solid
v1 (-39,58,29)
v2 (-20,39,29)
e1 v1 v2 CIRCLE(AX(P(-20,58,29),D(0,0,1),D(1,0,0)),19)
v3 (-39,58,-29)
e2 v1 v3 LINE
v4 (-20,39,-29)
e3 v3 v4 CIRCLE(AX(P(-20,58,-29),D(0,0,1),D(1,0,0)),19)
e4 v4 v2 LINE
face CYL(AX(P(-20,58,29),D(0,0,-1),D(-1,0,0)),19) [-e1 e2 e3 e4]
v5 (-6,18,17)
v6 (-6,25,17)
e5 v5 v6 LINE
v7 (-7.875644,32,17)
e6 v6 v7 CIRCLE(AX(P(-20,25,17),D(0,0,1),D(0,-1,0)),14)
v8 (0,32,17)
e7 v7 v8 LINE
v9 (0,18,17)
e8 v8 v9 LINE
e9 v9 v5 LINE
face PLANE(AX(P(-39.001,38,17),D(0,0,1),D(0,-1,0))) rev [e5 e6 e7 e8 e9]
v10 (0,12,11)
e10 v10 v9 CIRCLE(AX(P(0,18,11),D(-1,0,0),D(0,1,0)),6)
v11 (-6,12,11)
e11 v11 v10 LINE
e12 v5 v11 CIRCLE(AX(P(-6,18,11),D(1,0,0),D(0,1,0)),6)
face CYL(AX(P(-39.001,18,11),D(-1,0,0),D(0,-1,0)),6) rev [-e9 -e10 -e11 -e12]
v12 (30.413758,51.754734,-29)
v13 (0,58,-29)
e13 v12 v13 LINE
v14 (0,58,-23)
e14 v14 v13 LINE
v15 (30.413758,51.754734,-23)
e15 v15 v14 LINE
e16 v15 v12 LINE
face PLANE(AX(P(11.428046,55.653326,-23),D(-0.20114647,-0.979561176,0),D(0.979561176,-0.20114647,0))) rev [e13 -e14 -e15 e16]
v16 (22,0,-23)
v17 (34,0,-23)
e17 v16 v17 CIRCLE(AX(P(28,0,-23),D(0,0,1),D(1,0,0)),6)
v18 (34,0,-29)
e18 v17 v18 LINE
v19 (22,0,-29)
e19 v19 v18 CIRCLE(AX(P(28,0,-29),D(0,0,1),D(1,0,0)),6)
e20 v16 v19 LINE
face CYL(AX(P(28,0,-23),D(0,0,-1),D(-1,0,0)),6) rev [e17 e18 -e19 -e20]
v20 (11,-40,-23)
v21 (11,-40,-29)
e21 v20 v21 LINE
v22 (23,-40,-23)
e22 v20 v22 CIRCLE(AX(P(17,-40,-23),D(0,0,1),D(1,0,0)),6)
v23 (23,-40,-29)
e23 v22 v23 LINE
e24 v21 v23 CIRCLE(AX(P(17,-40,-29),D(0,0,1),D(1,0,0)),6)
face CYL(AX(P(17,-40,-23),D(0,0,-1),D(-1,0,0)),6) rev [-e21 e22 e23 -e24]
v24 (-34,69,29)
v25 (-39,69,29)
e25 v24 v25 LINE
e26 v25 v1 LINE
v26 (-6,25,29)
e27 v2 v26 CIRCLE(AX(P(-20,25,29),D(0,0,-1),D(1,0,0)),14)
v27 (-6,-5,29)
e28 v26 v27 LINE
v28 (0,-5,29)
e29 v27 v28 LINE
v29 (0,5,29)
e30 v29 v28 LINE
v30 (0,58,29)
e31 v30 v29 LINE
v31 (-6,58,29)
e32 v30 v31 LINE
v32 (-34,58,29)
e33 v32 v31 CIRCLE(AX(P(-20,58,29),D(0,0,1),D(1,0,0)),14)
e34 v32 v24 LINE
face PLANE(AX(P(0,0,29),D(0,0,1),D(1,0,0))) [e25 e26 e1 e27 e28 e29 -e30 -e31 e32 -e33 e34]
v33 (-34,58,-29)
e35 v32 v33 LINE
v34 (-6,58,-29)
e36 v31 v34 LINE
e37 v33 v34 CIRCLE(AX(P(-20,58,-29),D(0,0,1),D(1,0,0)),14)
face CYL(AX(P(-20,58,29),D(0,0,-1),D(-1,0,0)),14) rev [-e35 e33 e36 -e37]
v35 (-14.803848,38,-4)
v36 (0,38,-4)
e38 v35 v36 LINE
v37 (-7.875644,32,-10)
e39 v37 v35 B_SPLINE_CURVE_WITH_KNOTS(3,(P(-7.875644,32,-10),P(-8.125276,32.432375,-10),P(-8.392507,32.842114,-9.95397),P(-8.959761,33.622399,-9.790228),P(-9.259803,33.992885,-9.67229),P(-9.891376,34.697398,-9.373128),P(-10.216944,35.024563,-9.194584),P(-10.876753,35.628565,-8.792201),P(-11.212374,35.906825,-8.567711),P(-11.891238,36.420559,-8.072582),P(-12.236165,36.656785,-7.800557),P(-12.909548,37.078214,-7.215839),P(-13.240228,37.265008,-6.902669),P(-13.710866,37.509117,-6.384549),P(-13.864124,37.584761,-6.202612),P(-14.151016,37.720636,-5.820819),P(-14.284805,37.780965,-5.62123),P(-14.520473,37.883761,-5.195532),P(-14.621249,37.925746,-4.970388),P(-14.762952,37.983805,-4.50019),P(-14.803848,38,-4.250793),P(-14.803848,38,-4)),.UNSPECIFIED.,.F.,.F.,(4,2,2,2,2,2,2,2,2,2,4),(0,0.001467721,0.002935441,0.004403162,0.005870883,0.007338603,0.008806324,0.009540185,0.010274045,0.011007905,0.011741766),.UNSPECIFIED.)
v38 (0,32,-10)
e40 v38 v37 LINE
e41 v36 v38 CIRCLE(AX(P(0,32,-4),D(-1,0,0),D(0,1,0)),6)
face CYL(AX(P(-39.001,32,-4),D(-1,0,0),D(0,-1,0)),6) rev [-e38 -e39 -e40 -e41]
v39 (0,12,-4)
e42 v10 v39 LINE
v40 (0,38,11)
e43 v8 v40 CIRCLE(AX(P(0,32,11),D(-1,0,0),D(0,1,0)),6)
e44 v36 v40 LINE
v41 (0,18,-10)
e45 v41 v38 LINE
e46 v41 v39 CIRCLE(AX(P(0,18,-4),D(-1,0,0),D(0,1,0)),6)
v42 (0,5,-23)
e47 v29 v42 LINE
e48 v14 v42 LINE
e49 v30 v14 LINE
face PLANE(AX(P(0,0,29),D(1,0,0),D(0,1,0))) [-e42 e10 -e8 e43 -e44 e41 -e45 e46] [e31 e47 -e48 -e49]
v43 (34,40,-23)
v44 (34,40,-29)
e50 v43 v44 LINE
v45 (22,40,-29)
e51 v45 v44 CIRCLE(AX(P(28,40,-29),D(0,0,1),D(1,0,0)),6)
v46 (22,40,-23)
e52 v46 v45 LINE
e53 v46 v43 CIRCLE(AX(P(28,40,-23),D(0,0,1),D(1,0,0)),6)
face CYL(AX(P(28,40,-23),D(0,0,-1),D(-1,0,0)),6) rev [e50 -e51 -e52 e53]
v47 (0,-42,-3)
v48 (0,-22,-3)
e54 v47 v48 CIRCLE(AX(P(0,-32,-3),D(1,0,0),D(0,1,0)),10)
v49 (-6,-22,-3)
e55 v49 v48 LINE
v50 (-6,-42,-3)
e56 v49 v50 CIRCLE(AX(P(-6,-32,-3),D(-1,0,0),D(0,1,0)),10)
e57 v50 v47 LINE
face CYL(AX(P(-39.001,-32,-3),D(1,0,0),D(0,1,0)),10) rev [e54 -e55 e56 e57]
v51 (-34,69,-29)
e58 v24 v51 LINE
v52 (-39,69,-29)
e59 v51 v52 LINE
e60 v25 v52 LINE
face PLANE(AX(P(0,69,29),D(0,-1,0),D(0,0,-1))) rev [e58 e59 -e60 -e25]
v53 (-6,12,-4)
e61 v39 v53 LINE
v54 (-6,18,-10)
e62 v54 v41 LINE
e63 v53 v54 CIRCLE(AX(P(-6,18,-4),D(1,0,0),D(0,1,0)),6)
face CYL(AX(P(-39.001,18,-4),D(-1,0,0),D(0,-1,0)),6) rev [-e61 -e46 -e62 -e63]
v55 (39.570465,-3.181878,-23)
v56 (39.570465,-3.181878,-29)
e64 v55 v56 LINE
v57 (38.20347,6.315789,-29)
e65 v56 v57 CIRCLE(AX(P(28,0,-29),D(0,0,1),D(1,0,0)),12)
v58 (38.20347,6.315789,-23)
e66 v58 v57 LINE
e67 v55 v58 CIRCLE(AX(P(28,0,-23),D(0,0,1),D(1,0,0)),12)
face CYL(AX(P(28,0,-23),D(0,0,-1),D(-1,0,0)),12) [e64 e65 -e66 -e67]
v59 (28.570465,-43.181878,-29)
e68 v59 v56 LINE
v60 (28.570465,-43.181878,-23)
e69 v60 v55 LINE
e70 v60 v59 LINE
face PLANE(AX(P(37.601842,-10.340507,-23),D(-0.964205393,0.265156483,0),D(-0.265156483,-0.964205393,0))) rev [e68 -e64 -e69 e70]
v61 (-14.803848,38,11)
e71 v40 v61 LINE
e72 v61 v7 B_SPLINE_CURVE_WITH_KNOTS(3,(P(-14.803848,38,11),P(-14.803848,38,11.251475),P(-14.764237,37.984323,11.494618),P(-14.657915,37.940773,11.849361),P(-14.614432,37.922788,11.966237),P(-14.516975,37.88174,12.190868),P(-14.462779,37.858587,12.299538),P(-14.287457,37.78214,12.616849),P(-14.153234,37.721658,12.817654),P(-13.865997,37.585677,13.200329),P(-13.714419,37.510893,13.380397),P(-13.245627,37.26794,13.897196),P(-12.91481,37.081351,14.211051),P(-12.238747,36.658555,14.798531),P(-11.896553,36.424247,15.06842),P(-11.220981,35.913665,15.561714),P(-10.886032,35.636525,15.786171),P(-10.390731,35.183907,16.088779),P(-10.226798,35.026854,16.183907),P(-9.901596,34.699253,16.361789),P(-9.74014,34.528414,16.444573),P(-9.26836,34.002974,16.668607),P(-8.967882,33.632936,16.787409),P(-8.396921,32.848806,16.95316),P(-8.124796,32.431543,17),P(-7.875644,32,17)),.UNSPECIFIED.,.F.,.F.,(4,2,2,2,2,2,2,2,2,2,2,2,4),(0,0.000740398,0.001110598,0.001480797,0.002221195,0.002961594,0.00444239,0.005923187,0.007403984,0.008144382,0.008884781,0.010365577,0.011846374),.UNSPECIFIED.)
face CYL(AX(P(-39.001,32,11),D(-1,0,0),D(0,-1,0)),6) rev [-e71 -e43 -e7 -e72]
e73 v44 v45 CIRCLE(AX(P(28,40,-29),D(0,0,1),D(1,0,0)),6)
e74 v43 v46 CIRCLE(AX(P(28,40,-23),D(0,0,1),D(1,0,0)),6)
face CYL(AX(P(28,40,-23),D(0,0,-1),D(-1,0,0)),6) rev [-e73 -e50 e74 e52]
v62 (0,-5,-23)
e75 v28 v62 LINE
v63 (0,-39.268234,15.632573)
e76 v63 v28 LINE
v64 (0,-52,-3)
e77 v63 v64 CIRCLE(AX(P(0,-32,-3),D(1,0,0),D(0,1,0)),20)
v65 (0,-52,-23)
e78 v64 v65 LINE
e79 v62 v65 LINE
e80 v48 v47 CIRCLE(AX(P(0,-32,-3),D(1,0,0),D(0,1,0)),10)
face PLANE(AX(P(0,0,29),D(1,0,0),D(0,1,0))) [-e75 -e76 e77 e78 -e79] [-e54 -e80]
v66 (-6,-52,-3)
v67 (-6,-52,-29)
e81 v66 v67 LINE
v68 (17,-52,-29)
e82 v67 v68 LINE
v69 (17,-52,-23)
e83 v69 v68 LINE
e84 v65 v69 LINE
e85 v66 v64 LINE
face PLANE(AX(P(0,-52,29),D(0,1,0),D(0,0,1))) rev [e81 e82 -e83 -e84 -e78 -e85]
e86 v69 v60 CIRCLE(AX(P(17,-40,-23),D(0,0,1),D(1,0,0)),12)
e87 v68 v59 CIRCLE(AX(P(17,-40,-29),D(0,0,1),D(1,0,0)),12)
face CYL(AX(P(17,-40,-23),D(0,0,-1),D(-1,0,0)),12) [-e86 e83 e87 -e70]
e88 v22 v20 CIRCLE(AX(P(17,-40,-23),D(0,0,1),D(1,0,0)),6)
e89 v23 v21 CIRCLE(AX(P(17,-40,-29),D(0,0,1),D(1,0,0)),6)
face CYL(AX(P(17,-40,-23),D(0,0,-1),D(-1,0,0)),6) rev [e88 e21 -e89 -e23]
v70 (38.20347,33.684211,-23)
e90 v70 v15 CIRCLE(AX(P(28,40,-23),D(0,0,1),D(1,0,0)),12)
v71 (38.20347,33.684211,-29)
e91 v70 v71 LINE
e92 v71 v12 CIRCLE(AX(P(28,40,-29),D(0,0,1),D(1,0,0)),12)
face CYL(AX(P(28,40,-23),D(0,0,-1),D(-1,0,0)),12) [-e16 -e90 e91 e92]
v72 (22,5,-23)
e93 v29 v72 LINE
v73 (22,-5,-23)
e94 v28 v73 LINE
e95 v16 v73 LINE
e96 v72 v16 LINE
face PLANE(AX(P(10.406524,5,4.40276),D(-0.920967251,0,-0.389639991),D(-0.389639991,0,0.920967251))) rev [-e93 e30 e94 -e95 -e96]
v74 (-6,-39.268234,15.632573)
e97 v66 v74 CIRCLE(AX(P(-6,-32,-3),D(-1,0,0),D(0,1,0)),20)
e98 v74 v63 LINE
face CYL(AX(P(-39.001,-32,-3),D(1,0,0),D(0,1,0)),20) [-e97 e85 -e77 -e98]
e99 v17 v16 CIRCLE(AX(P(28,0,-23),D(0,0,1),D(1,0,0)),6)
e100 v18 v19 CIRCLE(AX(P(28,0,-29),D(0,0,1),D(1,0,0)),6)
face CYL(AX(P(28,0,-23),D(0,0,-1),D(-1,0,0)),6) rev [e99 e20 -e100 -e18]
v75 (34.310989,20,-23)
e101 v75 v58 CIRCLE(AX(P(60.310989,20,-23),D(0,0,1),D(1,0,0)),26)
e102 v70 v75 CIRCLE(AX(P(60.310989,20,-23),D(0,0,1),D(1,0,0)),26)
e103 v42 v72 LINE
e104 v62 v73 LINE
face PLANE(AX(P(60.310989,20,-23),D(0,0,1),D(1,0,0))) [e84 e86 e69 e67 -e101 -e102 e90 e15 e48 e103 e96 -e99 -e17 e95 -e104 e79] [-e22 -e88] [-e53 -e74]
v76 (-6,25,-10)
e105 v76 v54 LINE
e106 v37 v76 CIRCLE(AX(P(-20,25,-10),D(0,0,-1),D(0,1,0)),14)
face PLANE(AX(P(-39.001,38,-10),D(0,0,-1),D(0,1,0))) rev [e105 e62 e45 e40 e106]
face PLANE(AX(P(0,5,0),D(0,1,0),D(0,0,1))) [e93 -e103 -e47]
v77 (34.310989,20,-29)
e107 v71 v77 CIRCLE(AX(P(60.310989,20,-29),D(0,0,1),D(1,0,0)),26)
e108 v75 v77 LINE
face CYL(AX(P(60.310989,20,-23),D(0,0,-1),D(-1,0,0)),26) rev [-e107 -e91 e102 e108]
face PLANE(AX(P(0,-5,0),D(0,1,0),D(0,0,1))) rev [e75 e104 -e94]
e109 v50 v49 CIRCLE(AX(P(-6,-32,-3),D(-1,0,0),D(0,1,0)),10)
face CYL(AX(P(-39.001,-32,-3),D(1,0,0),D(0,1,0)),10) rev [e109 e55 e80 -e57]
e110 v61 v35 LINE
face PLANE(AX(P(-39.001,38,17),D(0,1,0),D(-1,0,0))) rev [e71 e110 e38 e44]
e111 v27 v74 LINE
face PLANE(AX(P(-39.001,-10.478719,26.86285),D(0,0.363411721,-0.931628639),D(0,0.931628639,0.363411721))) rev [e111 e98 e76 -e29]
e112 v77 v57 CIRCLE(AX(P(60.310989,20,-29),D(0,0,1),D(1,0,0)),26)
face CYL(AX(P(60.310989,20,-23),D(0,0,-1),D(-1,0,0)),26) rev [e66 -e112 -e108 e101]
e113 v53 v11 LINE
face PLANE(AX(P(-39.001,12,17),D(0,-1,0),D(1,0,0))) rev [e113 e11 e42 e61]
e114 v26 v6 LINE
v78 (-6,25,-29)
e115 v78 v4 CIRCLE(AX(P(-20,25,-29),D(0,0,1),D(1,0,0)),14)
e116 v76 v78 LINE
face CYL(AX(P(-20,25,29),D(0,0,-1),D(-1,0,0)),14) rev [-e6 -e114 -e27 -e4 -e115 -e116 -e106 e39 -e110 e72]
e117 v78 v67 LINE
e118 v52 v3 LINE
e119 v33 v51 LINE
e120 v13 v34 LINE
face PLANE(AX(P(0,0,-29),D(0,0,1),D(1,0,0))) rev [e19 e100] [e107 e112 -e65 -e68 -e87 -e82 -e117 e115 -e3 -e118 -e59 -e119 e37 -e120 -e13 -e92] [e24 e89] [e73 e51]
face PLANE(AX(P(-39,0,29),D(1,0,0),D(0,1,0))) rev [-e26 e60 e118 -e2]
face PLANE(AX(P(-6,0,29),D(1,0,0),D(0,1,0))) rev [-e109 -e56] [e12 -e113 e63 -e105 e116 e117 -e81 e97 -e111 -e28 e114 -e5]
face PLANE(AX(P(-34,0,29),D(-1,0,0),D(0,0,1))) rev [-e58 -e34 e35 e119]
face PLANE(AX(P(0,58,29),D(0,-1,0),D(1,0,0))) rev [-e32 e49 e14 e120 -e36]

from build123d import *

# Parameters (mm, degrees)
BRACKET_PROFILE_SKETCH_W  = 5
BRACKET_PROFILE_SKETCH_H  = 11
BRACKET_BODY_DEPTH        = 29
SADDLE_START              = -29
SKETCH1_4_R               = 6
SADDLE_STRAP_DEPTH        = 6
SQUARE_WINDOW_20X20_REACH = 86.865
SQUARE_WINDOW_SKETCH_R    = 10
CENTRE_GUSSET_DEPTH       = 5
CORNER_FILLET_R14_R       = 14
EDGE_NOTCH_REACH          = 86.865
EDGE_NOTCH_SKETCH_W       = 27
EDGE_NOTCH_SKETCH_H       = 26
NOTCH_FILLET_R6_R         = 6


with BuildPart() as part:
    # Bracket Profile Sketch → Bracket Body (new, symmetric)
    with BuildSketch(Plane.XY):
        with BuildLine():
            Line((0, -52), (0, 58))
            Line((0, 58), (-6, 58))
            ThreePointArc((-6, 58), (-20, 44), (-34, 58))
            Line((-34, 58), (-39, 58))
            ThreePointArc((-39, 58), (-26.892024376, 40.29406879), (-6, 45.154767421))
            Line((-6, 45.154767421), (-6, -52))
            Line((-6, -52), (0, -52))
        make_face()
        with Locations((-36.5, 63.5)):
            Rectangle(BRACKET_PROFILE_SKETCH_W, BRACKET_PROFILE_SKETCH_H)
    extrude(amount=BRACKET_BODY_DEPTH, both=True)

    # Sketch1_4 → Saddle Strap (add)
    with BuildSketch(Plane.XY.offset(SADDLE_START)):
        with BuildLine():
            ThreePointArc((38.203470161, 33.684210526), (34.310988843, 20), (38.203470161, 6.315789474))
            ThreePointArc((38.203470161, 6.315789474), (39.877604172, 1.709537694), (39.570464714, -3.181877796))
            Line((39.570464714, -3.181877796), (28.570464714, -43.181877796))
            ThreePointArc((28.570464714, -43.181877796), (24.27383896, -49.544174494), (17, -52))
            Line((17, -52), (0, -52))
            Line((0, -52), (0, 58))
            Line((0, 58), (30.413757643, 51.754734112))
            ThreePointArc((30.413757643, 51.754734112), (39.019735252, 44.750308934), (38.203470161, 33.684210526))
        make_face()
        with Locations((28, 40)):
            Circle(SKETCH1_4_R, mode=Mode.SUBTRACT)
        with Locations((28, 0)):
            Circle(SKETCH1_4_R, mode=Mode.SUBTRACT)
        with Locations((17, -40)):
            Circle(SKETCH1_4_R, mode=Mode.SUBTRACT)
    extrude(amount=SADDLE_STRAP_DEPTH)

    # Square Window Sketch → Square Window 20x20 (cut, up to next)
    with BuildSketch(Plane(origin=(0, 0, 0), x_dir=(0, 0, -1), z_dir=(1, 0, 0)), mode=Mode.PRIVATE) as square_window_20x20_sk1:
        with BuildLine():
            ThreePointArc((3, -52), (-8.283512569, -48.513096139), (-15.632572784, -39.268234411))
            Line((-15.632572784, -39.268234411), (-29, -5))
            Line((-29, -5), (-29, -52))
            Line((-29, -52), (3, -52))
        make_face()
    square_window_20x20_tool1 = extrude(square_window_20x20_sk1.sketch, amount=-SQUARE_WINDOW_20X20_REACH, mode=Mode.PRIVATE) & part.part
    # Square Window Sketch → Square Window 20x20 (cut, up to next)
    with BuildSketch(Plane(origin=(0, 0, 0), x_dir=(0, 0, -1), z_dir=(1, 0, 0)), mode=Mode.PRIVATE) as square_window_20x20_sk2:
        with Locations(Location((3, -32, 0), (0, 0, 90))):
            Circle(SQUARE_WINDOW_SKETCH_R)
    square_window_20x20_tool2 = extrude(square_window_20x20_sk2.sketch, amount=-SQUARE_WINDOW_20X20_REACH, mode=Mode.PRIVATE) & part.part
    add(square_window_20x20_tool1.solids().sort_by_distance((0, -37.269178, 21.871829))[0], mode=Mode.SUBTRACT)
    add(square_window_20x20_tool2.solids().sort_by_distance((0, -32, -3))[0], mode=Mode.SUBTRACT)

    # Centre Gusset Sketch → Centre Gusset (add, symmetric)
    with BuildSketch(Plane(origin=(0, 0, 0), x_dir=(1, 0, 0), z_dir=(0, 1, 0))):
        Polygon((0, 23), (0, -29), (22, 23), align=None)
    extrude(amount=CENTRE_GUSSET_DEPTH, both=True)

    # Corner Fillet R14
    corner_fillet_r14_edges = [part.edges().sort_by_distance(p)[0] for p in [
        (-6, 45.154767421, 0),
    ]]
    fillet(corner_fillet_r14_edges, radius=CORNER_FILLET_R14_R)

    # Edge Notch Sketch → Edge Notch (cut, up to next)
    with BuildSketch(Plane(origin=(0, 0, 0), x_dir=(0, 0, -1), z_dir=(1, 0, 0)), mode=Mode.PRIVATE) as edge_notch_sk1:
        with Locations((-3.5, 25)):
            Rectangle(EDGE_NOTCH_SKETCH_W, EDGE_NOTCH_SKETCH_H)
    edge_notch_tool1 = extrude(edge_notch_sk1.sketch, amount=-EDGE_NOTCH_REACH, mode=Mode.PRIVATE) & part.part
    add(edge_notch_tool1.solids().sort_by_distance((0, 25, 3.5))[0], mode=Mode.SUBTRACT)

    # Notch Fillet R6
    notch_fillet_r6_edges = [part.edges().sort_by_distance(p)[0] for p in [
        (-7.401923789, 38, 17),
        (-3, 12, -10),
        (-3, 12, 17),
        (-7.401923789, 38, -10),
    ]]
    fillet(notch_fillet_r6_edges, radius=NOTCH_FILLET_R6_R)


solid = part.part
